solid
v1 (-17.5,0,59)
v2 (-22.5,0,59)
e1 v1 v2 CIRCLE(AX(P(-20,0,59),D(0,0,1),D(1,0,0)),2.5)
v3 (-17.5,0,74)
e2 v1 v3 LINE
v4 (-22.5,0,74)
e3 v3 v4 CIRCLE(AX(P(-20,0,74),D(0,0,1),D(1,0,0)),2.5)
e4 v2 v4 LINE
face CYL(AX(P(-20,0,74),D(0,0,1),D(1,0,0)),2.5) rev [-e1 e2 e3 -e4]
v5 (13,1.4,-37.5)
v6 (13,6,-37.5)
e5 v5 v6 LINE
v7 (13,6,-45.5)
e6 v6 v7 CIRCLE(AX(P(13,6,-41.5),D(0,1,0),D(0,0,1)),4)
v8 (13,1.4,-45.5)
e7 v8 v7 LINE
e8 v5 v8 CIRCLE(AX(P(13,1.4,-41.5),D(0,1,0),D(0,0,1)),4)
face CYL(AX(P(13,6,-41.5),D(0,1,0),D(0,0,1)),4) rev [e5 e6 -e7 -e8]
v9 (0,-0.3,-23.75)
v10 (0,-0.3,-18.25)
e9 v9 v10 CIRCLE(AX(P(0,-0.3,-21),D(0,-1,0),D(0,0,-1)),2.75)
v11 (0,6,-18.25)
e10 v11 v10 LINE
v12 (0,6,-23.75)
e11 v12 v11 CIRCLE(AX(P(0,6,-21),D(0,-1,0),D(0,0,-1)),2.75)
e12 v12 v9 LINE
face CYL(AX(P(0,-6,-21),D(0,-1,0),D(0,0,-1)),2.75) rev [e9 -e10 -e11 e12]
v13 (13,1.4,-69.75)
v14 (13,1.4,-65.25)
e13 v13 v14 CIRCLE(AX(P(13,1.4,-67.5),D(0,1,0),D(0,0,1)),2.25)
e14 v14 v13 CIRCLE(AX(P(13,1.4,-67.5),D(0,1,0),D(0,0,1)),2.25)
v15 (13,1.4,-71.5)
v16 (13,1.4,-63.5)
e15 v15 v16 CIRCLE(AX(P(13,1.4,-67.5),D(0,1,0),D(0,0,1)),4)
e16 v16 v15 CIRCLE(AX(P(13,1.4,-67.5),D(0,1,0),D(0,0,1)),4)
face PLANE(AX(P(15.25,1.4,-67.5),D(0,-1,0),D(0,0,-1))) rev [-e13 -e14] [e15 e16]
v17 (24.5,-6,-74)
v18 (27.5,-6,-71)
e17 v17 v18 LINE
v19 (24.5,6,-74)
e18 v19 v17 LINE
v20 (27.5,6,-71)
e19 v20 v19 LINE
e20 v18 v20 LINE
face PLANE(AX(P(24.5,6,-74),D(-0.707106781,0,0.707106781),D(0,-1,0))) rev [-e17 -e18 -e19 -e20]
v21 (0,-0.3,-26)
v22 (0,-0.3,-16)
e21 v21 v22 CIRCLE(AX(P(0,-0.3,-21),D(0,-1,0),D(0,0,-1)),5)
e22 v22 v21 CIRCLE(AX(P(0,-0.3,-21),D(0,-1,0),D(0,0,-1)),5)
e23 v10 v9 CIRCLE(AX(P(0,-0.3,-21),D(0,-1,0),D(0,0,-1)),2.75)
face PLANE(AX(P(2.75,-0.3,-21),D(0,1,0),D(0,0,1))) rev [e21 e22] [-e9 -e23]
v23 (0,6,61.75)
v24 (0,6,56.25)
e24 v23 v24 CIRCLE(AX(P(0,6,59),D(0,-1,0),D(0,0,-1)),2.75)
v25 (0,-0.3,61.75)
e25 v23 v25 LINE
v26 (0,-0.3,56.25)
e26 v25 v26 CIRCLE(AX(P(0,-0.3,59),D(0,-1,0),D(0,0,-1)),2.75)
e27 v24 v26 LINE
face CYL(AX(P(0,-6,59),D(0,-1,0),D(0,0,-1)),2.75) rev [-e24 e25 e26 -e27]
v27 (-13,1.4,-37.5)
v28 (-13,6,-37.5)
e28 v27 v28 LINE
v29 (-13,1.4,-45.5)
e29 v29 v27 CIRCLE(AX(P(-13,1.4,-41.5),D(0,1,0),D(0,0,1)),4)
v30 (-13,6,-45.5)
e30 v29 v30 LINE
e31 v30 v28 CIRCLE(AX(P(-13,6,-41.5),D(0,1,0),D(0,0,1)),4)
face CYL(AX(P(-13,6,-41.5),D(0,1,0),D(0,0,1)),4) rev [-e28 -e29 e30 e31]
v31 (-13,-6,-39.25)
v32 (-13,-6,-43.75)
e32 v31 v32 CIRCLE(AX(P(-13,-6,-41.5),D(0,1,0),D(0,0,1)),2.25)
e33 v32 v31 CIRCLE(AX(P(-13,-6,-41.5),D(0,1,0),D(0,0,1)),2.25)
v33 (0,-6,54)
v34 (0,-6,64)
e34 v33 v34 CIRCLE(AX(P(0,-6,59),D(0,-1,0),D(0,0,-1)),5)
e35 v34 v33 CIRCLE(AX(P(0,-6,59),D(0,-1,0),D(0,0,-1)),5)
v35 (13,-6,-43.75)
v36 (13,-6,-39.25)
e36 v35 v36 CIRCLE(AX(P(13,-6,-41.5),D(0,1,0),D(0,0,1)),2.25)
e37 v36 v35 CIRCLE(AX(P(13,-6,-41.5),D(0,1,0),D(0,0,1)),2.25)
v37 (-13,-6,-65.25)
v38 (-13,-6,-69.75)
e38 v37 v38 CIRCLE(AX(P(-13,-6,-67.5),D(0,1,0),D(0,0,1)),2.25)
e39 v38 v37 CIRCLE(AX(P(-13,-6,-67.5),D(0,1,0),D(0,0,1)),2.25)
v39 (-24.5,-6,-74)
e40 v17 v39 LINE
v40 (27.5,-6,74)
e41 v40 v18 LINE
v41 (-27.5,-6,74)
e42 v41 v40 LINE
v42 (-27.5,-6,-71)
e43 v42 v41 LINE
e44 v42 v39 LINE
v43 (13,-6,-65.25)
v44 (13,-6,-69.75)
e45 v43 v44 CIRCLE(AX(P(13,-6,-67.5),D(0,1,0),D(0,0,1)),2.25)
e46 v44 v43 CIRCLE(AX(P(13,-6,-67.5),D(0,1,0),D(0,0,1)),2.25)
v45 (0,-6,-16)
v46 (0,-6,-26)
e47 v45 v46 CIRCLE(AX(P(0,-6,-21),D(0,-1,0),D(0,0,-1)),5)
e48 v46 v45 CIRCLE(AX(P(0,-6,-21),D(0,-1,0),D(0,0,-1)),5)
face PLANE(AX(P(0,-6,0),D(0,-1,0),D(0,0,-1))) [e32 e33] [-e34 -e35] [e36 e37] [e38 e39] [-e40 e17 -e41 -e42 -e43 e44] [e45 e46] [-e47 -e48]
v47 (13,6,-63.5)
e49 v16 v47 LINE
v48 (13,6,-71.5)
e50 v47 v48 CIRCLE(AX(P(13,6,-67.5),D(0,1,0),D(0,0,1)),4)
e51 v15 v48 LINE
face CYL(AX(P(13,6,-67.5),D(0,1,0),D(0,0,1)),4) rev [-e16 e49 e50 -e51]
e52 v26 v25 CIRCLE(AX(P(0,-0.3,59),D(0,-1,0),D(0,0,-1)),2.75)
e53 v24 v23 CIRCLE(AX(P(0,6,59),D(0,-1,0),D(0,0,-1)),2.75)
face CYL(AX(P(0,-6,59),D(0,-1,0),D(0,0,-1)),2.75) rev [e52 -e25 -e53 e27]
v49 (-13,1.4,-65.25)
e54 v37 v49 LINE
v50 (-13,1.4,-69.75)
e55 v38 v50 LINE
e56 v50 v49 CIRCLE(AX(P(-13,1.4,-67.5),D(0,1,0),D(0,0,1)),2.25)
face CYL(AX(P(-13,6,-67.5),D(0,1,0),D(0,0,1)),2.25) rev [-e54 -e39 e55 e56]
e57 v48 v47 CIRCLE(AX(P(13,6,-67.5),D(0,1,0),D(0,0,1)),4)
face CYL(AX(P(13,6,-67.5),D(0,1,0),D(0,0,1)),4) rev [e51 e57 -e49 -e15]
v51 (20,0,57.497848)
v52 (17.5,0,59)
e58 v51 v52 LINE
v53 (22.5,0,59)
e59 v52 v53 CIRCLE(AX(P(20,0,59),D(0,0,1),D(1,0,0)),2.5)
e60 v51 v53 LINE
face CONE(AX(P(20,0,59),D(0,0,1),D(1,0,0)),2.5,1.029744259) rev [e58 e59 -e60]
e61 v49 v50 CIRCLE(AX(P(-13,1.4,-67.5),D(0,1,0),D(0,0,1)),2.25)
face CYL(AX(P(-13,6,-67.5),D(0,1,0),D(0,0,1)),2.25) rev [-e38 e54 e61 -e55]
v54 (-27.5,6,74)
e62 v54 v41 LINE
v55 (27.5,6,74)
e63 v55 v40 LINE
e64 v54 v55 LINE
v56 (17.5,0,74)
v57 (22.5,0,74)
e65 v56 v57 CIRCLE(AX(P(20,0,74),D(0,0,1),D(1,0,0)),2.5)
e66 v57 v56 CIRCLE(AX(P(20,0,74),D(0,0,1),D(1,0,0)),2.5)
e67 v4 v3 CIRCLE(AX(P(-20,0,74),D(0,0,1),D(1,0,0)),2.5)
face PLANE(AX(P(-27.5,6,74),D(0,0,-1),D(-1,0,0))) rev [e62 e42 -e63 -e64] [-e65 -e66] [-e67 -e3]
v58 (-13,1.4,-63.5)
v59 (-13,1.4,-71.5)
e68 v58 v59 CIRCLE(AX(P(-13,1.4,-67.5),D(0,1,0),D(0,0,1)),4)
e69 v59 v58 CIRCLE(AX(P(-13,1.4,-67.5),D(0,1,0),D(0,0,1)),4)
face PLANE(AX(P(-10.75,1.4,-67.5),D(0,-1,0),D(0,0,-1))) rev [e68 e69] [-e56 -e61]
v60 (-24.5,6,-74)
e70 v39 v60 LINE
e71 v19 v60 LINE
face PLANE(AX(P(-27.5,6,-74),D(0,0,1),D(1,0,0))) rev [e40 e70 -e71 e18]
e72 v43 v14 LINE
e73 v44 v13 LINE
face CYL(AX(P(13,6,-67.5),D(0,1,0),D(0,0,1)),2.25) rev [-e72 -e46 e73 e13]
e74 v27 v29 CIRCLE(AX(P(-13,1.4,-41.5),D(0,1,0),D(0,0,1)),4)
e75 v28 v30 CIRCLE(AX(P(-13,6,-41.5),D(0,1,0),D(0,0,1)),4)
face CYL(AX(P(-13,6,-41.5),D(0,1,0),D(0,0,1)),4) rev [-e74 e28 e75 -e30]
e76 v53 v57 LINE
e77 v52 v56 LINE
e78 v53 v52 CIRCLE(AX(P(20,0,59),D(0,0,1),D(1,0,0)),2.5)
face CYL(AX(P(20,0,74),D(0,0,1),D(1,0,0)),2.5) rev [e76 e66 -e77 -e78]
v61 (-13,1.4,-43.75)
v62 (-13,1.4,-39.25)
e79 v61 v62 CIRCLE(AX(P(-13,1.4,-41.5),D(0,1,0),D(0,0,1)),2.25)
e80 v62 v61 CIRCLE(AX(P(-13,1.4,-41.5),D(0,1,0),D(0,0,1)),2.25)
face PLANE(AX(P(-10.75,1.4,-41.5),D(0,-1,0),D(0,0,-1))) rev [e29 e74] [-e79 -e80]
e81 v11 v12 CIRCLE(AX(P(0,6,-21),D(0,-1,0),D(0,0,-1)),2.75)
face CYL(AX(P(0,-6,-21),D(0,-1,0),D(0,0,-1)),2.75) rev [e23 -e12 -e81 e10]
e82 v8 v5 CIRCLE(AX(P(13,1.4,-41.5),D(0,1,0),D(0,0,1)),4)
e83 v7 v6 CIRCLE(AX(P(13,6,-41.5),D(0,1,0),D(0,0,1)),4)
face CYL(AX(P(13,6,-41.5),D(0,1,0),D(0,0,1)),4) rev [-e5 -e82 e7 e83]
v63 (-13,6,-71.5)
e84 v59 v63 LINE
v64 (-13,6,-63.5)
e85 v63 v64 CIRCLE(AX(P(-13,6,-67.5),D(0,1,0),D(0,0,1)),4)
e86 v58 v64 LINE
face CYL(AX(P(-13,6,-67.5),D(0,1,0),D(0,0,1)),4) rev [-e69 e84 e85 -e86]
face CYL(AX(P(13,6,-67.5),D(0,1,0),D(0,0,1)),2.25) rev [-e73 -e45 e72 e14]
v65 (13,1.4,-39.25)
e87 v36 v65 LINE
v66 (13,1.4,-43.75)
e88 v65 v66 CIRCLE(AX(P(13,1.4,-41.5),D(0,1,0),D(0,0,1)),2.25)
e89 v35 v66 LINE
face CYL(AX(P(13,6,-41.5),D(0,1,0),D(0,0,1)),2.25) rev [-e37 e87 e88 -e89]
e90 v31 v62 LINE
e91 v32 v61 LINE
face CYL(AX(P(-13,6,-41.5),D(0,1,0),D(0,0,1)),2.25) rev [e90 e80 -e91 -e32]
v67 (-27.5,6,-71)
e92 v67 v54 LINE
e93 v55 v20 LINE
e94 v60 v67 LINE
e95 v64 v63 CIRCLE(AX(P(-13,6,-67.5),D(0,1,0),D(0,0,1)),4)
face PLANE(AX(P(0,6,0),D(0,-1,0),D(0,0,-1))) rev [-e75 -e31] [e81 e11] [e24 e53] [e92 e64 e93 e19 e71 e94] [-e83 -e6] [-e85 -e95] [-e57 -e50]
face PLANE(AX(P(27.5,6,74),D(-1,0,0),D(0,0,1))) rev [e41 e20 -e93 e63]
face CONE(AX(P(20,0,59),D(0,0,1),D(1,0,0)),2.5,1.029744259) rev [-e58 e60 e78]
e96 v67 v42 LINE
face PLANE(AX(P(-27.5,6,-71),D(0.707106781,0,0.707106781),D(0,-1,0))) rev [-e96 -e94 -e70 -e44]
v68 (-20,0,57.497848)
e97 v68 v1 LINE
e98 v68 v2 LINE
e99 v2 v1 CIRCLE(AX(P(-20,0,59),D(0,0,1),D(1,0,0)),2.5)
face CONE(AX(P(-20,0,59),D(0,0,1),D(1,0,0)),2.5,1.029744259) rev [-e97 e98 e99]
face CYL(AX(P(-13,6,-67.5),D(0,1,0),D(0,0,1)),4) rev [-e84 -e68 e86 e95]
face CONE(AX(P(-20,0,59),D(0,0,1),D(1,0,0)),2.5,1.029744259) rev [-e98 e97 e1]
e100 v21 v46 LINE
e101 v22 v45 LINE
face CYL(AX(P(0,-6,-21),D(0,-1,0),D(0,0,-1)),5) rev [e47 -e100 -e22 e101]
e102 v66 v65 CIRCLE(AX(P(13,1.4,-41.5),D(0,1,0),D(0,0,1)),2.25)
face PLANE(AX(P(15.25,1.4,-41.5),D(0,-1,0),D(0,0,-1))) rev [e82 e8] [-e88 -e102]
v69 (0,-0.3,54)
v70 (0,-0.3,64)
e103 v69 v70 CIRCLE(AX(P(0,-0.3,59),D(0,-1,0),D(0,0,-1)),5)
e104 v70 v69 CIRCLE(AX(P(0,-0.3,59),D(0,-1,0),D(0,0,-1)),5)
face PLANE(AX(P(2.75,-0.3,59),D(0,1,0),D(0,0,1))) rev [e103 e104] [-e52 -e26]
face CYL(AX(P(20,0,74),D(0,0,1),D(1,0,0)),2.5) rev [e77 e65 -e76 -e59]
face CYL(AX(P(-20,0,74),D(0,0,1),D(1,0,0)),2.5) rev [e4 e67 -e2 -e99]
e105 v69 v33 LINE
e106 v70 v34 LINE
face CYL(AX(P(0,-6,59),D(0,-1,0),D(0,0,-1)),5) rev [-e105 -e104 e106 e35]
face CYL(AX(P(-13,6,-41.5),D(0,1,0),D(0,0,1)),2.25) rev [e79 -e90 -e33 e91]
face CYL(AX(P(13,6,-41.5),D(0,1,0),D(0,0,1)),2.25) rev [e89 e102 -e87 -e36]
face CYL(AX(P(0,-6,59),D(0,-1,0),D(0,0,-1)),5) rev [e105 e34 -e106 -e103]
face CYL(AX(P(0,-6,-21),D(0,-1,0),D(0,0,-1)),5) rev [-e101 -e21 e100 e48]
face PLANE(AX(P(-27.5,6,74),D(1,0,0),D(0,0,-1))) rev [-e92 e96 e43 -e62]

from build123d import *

# Parameters (mm, degrees)
SKETCH_1_W                = 55
SKETCH_1_H                = 148
EXTRUDE_1_DEPTH           = 6
CHAMFER_1_SIZE            = 3
HOLE_WIZARD_1_D           = 4.5
HOLE_WIZARD_1_CBORE_D     = 8
HOLE_WIZARD_1_CBORE_DEPTH = 4.6
HOLE_WIZARD_M6_1_D        = 5
HOLE_WIZARD_M6_1_DEPTH    = 15
HOLE_WIZARD_M6_1_TIP      = 1.502151548
HOLE_WIZARD_2_D           = 5.5
HOLE_WIZARD_2_CBORE_D     = 10
HOLE_WIZARD_2_CBORE_DEPTH = 5.7


with BuildPart() as part:
    # 草图1 → 凸台-拉伸1 (new, symmetric)
    with BuildSketch(Plane(origin=(0, 0, 0), x_dir=(1, 0, 0), z_dir=(0, 1, 0))):
        Rectangle(SKETCH_1_W, SKETCH_1_H)
    extrude(amount=EXTRUDE_1_DEPTH, both=True)

    # 倒角1
    chamfer_1_edges = [part.edges().sort_by_distance(p)[0] for p in [
        (-27.5, 0, -74),
        (27.5, 0, -74),
    ]]
    chamfer(chamfer_1_edges, length=CHAMFER_1_SIZE)

    # 打孔尺寸(%根据)内六角圆柱头螺钉的类型1 (through all)
    with Locations(Plane(origin=(0, 6, 0), x_dir=(1, 0, 0), z_dir=(0, 1, 0))):
        with Locations((13, 41.5), (13, 67.5), (-13, 67.5), (-13, 41.5)):
            CounterBoreHole(HOLE_WIZARD_1_D / 2, HOLE_WIZARD_1_CBORE_D / 2, HOLE_WIZARD_1_CBORE_DEPTH)

    # M6 螺纹孔1
    with Locations(Plane.XY.offset(74)):
        with Locations((20, 0), (-20, 0)):
            Hole(HOLE_WIZARD_M6_1_D / 2, depth=HOLE_WIZARD_M6_1_DEPTH)
            with Locations((0, 0, -(HOLE_WIZARD_M6_1_DEPTH + HOLE_WIZARD_M6_1_TIP / 2))):  # 118° drill point
                Cone(0, HOLE_WIZARD_M6_1_D / 2, HOLE_WIZARD_M6_1_TIP, mode=Mode.SUBTRACT)

    # 打孔尺寸(%根据)内六角圆柱头螺钉的类型2 (through all)
    with Locations(Plane.XZ.offset(6)):
        with Locations((0, 59), (0, -21)):
            CounterBoreHole(HOLE_WIZARD_2_D / 2, HOLE_WIZARD_2_CBORE_D / 2, HOLE_WIZARD_2_CBORE_DEPTH)


solid = part.part
